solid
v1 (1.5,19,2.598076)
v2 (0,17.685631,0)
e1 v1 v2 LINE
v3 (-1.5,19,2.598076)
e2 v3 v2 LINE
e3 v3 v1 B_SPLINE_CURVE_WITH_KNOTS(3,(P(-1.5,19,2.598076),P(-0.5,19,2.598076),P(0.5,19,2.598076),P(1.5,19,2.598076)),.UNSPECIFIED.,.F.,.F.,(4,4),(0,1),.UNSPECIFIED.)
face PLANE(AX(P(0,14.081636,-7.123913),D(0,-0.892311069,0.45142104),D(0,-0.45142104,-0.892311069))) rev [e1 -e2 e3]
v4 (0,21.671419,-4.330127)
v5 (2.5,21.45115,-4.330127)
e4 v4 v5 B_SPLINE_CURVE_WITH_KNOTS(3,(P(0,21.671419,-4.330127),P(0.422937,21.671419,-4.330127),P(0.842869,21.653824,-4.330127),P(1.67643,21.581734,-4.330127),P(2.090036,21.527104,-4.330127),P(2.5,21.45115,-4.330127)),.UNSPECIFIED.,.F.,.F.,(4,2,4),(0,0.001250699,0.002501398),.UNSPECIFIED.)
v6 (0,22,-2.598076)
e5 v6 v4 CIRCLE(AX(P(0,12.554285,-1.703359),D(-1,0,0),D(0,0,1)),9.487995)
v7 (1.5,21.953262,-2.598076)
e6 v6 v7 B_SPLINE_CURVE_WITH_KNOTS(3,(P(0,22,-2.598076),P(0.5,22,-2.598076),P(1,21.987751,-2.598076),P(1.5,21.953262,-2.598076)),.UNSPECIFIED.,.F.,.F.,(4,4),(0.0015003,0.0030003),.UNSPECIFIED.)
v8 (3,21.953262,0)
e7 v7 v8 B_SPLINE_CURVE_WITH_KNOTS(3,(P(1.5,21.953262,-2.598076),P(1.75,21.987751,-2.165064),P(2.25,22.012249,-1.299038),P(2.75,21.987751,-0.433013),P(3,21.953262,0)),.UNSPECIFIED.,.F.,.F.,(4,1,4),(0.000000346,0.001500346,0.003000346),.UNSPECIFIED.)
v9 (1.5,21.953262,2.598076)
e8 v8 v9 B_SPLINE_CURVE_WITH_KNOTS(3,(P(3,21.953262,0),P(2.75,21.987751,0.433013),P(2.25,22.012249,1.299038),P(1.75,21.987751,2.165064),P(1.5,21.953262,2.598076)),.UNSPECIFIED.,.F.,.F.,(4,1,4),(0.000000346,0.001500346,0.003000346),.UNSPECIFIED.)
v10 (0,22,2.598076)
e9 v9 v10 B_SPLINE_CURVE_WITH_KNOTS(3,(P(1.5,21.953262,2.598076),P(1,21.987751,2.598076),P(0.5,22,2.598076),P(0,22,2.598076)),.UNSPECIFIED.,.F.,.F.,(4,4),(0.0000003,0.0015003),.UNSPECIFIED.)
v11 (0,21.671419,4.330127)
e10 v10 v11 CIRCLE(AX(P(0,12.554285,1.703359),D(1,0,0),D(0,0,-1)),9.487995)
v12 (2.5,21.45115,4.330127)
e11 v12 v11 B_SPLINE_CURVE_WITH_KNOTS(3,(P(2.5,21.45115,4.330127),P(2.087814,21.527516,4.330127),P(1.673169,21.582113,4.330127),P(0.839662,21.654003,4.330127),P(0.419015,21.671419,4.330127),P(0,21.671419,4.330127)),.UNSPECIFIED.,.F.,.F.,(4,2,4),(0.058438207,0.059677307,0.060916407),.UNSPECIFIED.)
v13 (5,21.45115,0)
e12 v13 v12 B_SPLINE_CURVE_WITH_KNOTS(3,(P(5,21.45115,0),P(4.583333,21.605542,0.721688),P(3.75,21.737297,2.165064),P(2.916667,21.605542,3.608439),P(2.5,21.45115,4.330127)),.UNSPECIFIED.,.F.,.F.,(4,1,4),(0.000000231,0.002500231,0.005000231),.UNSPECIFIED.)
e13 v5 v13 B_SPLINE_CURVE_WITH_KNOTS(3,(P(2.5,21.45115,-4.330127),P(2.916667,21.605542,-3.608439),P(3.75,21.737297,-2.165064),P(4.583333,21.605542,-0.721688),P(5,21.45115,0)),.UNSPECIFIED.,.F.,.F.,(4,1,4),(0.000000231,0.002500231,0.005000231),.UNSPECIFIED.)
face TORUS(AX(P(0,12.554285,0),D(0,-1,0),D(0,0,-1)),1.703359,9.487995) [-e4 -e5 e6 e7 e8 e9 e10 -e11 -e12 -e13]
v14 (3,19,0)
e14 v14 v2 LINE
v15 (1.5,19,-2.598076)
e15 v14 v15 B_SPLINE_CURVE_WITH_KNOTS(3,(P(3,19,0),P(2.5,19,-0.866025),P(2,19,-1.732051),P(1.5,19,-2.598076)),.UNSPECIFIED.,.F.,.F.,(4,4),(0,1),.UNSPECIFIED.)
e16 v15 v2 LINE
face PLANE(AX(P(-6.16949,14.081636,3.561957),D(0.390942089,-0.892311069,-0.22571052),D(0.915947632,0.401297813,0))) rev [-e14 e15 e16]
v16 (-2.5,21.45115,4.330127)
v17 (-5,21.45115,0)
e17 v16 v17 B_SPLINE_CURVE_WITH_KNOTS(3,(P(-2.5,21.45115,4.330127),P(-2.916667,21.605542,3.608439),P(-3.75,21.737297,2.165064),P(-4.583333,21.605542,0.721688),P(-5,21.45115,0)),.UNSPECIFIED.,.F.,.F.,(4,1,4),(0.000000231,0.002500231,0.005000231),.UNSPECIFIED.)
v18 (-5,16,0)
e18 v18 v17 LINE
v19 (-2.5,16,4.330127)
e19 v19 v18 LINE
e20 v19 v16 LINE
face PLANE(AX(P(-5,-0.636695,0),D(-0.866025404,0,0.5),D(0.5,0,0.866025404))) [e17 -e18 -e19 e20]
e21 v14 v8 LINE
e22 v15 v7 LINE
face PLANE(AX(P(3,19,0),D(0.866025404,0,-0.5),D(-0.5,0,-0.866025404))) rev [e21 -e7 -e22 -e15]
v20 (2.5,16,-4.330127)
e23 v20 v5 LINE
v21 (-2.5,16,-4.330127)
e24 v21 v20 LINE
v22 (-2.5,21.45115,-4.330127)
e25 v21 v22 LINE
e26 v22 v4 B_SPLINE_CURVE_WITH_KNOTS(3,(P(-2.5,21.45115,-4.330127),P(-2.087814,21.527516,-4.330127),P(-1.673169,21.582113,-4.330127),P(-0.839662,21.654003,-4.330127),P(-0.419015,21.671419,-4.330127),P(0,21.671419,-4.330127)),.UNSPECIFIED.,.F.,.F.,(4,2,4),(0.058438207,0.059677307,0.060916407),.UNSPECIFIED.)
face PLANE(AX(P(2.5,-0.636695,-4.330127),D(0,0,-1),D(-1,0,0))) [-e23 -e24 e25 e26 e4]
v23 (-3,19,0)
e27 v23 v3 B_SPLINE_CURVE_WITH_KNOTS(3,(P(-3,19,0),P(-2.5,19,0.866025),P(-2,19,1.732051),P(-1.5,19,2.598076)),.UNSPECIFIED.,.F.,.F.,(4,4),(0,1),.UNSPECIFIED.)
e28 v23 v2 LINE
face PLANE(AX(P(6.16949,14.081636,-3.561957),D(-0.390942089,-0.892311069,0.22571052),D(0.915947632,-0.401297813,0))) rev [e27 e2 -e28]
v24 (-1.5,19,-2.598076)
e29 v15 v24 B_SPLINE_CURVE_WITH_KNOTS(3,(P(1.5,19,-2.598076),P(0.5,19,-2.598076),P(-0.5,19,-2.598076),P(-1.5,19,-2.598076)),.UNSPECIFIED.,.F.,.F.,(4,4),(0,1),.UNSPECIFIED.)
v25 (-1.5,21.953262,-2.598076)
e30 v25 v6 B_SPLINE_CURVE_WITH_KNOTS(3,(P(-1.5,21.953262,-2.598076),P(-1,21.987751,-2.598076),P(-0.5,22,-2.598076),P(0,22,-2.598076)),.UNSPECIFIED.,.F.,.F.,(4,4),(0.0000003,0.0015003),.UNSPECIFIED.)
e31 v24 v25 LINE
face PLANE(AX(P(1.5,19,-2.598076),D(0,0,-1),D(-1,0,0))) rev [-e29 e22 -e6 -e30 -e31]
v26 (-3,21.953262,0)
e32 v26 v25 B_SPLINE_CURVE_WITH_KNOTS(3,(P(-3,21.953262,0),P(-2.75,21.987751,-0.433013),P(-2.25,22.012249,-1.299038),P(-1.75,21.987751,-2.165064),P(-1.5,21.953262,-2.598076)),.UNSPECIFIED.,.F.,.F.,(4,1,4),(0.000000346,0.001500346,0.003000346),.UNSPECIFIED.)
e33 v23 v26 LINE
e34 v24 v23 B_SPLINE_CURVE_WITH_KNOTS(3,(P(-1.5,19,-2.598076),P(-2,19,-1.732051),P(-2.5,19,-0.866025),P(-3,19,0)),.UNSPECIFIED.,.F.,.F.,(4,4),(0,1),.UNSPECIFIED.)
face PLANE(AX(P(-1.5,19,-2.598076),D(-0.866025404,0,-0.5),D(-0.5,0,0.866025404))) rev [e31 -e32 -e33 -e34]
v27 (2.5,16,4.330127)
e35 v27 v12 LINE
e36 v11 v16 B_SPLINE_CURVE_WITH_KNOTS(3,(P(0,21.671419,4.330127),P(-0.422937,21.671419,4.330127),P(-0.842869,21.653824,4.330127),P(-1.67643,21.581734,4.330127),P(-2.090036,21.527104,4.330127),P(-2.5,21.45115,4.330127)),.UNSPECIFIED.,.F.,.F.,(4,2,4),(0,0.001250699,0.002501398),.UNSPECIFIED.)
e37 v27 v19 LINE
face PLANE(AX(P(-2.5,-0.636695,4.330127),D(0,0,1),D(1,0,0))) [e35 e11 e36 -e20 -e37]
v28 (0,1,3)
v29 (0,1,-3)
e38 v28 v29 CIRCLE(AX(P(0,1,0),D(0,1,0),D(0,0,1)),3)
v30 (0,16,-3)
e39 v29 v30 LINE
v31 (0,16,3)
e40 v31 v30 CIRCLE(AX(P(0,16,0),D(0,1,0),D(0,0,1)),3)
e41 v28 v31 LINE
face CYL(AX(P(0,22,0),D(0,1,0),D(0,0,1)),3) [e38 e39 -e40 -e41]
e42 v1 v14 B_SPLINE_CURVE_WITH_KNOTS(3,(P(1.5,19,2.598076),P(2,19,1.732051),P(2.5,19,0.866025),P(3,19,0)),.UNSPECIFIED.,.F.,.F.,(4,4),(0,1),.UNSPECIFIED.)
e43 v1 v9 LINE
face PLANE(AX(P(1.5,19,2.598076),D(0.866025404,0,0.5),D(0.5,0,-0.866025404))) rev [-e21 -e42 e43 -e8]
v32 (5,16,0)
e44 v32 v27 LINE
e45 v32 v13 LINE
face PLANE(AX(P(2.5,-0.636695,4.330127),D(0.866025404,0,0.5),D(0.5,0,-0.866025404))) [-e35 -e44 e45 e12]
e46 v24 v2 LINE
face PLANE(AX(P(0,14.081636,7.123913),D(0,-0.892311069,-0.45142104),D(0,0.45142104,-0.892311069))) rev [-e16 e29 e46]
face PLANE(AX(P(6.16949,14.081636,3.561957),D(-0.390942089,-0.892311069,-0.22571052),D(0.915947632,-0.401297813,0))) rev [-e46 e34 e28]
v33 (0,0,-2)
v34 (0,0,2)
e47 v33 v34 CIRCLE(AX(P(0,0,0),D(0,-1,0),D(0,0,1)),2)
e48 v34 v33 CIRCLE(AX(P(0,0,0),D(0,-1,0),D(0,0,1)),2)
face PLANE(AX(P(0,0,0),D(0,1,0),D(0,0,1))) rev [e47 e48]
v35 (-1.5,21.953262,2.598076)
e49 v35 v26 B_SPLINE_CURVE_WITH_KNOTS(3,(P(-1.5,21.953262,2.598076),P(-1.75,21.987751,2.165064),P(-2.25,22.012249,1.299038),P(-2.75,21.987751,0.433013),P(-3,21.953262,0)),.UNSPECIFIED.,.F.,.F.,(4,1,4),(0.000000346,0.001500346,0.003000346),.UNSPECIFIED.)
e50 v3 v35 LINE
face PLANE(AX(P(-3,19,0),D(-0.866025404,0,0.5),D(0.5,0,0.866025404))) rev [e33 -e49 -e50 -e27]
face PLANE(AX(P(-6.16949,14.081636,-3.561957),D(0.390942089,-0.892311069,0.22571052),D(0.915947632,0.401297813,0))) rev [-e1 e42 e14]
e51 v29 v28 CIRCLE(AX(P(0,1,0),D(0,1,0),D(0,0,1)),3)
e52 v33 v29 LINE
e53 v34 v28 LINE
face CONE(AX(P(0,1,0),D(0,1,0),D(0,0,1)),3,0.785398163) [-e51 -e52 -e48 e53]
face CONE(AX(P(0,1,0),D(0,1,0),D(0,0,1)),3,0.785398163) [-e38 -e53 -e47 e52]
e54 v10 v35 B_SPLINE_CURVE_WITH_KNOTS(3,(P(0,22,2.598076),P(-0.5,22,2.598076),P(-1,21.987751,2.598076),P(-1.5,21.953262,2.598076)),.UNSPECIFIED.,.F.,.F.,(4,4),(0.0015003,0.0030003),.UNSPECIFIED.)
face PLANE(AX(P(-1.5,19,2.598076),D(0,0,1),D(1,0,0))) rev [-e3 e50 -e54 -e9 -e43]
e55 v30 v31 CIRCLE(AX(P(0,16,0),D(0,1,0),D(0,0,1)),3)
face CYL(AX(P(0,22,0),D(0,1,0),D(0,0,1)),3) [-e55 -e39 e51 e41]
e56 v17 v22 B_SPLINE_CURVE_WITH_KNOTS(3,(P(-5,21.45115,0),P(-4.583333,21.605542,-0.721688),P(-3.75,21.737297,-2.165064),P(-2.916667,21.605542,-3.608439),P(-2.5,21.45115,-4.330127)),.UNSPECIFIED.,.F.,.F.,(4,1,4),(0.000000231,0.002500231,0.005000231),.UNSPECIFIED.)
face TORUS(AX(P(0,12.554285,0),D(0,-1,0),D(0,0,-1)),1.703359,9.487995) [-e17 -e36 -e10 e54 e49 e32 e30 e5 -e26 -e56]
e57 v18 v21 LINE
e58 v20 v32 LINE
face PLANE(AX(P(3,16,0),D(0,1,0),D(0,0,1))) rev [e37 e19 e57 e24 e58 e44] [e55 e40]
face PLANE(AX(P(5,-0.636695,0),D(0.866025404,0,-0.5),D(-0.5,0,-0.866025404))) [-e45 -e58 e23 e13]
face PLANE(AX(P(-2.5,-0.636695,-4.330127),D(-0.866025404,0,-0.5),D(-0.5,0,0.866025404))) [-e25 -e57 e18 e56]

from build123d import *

# Parameters (mm, degrees)
SKETCH2_W          = 12.434421081
SKETCH2_H          = 11.052818739
CUT_EXTRUDE2_DEPTH = 6
CUT_EXTRUDE3_DEPTH = 3
CHAMFER1_SIZE      = 1


with BuildPart() as part:
    # Sketch1 → Revolve1 (revolve)
    with BuildSketch(Plane.XY, mode=Mode.PRIVATE) as revolve1_sk:
        Polygon((0, 0), (3, 0), (3, 16), (5, 16), (5, 22), (0, 22), (0, 0.812520437), align=None)
    revolve(revolve1_sk.sketch.rotate(Axis((0, 22, 0), (0, -1, 0)), 90), axis=Axis((0, 22, 0), (0, -1, 0)))

    # Sketch2 → Cut-Extrude2 (cut)
    with BuildSketch(Plane(origin=(0, 22, 0), x_dir=(1, 0, 0), z_dir=(0, 1, 0))):
        with Locations((0.708980149, -0.054536934)):
            Rectangle(SKETCH2_W, SKETCH2_H)
        Polygon((5, 0), (2.5, 4.330127019), (-2.5, 4.330127019), (-5, 0), (-2.5, -4.330127019), (2.5, -4.330127019), align=None, mode=Mode.SUBTRACT)
    extrude(amount=-CUT_EXTRUDE2_DEPTH, mode=Mode.SUBTRACT)

    # Sketch3 → Cut-Extrude3 (cut)
    with BuildSketch(Plane(origin=(0, 22, 0), x_dir=(1, 0, 0), z_dir=(0, 1, 0))):
        Polygon((3, 0), (1.5, 2.598076211), (-1.5, 2.598076211), (-3, 0), (-1.5, -2.598076211), (1.5, -2.598076211), align=None)
    extrude(amount=-CUT_EXTRUDE3_DEPTH, mode=Mode.SUBTRACT)

    # Sketch5 → Cut-Loft1 section 0
    with BuildSketch(Plane(origin=(0, 19, 0), x_dir=(1, 0, 0), z_dir=(0, 1, 0)), mode=Mode.PRIVATE) as cut_loft1_s0:
        with BuildLine():
            Line((1.5, 2.598076211), (-1.5, 2.598076211))
            Line((-1.5, 2.598076211), (-3, 0))
            Line((-3, 0), (-1.5, -2.598076211))
            Line((-1.5, -2.598076211), (1.5, -2.598076211))
            Line((1.5, -2.598076211), (3, 0))
            Line((3, 0), (1.5, 2.598076211))
        make_face()
    loft([cut_loft1_s0.sketch, Vertex(0, 17.68563071, 0)], mode=Mode.SUBTRACT)

    # Chamfer1
    chamfer1_edges = [part.edges().sort_by_distance(p)[0] for p in [
        (0, 0, -3),
    ]]
    chamfer(chamfer1_edges, length=CHAMFER1_SIZE)

    # Sketch6 → Cut-Revolve1 (revolve, cut)
    with BuildSketch(Plane(origin=(0, 0, 0), x_dir=(0, 0, -1), z_dir=(1, 0, 0)), mode=Mode.PRIVATE) as cut_revolve1_sk:
        with BuildLine():
            Line((-5.464509536, 21.264956491), (-5.887873992, 22.169745092))
            Line((-5.887873992, 22.169745092), (-3.885003272, 23.64244415))
            Line((-3.885003272, 23.64244415), (-2.598076211, 22))
            ThreePointArc((-2.598076211, 22), (-4.060125505, 21.744916236), (-5.464509536, 21.264956491))
        make_face()
    revolve(cut_revolve1_sk.sketch.rotate(Axis((0, 16, 0), (0, 1, 0)), 149.999999986), axis=Axis((0, 16, 0), (0, 1, 0)), mode=Mode.SUBTRACT)


solid = part.part
